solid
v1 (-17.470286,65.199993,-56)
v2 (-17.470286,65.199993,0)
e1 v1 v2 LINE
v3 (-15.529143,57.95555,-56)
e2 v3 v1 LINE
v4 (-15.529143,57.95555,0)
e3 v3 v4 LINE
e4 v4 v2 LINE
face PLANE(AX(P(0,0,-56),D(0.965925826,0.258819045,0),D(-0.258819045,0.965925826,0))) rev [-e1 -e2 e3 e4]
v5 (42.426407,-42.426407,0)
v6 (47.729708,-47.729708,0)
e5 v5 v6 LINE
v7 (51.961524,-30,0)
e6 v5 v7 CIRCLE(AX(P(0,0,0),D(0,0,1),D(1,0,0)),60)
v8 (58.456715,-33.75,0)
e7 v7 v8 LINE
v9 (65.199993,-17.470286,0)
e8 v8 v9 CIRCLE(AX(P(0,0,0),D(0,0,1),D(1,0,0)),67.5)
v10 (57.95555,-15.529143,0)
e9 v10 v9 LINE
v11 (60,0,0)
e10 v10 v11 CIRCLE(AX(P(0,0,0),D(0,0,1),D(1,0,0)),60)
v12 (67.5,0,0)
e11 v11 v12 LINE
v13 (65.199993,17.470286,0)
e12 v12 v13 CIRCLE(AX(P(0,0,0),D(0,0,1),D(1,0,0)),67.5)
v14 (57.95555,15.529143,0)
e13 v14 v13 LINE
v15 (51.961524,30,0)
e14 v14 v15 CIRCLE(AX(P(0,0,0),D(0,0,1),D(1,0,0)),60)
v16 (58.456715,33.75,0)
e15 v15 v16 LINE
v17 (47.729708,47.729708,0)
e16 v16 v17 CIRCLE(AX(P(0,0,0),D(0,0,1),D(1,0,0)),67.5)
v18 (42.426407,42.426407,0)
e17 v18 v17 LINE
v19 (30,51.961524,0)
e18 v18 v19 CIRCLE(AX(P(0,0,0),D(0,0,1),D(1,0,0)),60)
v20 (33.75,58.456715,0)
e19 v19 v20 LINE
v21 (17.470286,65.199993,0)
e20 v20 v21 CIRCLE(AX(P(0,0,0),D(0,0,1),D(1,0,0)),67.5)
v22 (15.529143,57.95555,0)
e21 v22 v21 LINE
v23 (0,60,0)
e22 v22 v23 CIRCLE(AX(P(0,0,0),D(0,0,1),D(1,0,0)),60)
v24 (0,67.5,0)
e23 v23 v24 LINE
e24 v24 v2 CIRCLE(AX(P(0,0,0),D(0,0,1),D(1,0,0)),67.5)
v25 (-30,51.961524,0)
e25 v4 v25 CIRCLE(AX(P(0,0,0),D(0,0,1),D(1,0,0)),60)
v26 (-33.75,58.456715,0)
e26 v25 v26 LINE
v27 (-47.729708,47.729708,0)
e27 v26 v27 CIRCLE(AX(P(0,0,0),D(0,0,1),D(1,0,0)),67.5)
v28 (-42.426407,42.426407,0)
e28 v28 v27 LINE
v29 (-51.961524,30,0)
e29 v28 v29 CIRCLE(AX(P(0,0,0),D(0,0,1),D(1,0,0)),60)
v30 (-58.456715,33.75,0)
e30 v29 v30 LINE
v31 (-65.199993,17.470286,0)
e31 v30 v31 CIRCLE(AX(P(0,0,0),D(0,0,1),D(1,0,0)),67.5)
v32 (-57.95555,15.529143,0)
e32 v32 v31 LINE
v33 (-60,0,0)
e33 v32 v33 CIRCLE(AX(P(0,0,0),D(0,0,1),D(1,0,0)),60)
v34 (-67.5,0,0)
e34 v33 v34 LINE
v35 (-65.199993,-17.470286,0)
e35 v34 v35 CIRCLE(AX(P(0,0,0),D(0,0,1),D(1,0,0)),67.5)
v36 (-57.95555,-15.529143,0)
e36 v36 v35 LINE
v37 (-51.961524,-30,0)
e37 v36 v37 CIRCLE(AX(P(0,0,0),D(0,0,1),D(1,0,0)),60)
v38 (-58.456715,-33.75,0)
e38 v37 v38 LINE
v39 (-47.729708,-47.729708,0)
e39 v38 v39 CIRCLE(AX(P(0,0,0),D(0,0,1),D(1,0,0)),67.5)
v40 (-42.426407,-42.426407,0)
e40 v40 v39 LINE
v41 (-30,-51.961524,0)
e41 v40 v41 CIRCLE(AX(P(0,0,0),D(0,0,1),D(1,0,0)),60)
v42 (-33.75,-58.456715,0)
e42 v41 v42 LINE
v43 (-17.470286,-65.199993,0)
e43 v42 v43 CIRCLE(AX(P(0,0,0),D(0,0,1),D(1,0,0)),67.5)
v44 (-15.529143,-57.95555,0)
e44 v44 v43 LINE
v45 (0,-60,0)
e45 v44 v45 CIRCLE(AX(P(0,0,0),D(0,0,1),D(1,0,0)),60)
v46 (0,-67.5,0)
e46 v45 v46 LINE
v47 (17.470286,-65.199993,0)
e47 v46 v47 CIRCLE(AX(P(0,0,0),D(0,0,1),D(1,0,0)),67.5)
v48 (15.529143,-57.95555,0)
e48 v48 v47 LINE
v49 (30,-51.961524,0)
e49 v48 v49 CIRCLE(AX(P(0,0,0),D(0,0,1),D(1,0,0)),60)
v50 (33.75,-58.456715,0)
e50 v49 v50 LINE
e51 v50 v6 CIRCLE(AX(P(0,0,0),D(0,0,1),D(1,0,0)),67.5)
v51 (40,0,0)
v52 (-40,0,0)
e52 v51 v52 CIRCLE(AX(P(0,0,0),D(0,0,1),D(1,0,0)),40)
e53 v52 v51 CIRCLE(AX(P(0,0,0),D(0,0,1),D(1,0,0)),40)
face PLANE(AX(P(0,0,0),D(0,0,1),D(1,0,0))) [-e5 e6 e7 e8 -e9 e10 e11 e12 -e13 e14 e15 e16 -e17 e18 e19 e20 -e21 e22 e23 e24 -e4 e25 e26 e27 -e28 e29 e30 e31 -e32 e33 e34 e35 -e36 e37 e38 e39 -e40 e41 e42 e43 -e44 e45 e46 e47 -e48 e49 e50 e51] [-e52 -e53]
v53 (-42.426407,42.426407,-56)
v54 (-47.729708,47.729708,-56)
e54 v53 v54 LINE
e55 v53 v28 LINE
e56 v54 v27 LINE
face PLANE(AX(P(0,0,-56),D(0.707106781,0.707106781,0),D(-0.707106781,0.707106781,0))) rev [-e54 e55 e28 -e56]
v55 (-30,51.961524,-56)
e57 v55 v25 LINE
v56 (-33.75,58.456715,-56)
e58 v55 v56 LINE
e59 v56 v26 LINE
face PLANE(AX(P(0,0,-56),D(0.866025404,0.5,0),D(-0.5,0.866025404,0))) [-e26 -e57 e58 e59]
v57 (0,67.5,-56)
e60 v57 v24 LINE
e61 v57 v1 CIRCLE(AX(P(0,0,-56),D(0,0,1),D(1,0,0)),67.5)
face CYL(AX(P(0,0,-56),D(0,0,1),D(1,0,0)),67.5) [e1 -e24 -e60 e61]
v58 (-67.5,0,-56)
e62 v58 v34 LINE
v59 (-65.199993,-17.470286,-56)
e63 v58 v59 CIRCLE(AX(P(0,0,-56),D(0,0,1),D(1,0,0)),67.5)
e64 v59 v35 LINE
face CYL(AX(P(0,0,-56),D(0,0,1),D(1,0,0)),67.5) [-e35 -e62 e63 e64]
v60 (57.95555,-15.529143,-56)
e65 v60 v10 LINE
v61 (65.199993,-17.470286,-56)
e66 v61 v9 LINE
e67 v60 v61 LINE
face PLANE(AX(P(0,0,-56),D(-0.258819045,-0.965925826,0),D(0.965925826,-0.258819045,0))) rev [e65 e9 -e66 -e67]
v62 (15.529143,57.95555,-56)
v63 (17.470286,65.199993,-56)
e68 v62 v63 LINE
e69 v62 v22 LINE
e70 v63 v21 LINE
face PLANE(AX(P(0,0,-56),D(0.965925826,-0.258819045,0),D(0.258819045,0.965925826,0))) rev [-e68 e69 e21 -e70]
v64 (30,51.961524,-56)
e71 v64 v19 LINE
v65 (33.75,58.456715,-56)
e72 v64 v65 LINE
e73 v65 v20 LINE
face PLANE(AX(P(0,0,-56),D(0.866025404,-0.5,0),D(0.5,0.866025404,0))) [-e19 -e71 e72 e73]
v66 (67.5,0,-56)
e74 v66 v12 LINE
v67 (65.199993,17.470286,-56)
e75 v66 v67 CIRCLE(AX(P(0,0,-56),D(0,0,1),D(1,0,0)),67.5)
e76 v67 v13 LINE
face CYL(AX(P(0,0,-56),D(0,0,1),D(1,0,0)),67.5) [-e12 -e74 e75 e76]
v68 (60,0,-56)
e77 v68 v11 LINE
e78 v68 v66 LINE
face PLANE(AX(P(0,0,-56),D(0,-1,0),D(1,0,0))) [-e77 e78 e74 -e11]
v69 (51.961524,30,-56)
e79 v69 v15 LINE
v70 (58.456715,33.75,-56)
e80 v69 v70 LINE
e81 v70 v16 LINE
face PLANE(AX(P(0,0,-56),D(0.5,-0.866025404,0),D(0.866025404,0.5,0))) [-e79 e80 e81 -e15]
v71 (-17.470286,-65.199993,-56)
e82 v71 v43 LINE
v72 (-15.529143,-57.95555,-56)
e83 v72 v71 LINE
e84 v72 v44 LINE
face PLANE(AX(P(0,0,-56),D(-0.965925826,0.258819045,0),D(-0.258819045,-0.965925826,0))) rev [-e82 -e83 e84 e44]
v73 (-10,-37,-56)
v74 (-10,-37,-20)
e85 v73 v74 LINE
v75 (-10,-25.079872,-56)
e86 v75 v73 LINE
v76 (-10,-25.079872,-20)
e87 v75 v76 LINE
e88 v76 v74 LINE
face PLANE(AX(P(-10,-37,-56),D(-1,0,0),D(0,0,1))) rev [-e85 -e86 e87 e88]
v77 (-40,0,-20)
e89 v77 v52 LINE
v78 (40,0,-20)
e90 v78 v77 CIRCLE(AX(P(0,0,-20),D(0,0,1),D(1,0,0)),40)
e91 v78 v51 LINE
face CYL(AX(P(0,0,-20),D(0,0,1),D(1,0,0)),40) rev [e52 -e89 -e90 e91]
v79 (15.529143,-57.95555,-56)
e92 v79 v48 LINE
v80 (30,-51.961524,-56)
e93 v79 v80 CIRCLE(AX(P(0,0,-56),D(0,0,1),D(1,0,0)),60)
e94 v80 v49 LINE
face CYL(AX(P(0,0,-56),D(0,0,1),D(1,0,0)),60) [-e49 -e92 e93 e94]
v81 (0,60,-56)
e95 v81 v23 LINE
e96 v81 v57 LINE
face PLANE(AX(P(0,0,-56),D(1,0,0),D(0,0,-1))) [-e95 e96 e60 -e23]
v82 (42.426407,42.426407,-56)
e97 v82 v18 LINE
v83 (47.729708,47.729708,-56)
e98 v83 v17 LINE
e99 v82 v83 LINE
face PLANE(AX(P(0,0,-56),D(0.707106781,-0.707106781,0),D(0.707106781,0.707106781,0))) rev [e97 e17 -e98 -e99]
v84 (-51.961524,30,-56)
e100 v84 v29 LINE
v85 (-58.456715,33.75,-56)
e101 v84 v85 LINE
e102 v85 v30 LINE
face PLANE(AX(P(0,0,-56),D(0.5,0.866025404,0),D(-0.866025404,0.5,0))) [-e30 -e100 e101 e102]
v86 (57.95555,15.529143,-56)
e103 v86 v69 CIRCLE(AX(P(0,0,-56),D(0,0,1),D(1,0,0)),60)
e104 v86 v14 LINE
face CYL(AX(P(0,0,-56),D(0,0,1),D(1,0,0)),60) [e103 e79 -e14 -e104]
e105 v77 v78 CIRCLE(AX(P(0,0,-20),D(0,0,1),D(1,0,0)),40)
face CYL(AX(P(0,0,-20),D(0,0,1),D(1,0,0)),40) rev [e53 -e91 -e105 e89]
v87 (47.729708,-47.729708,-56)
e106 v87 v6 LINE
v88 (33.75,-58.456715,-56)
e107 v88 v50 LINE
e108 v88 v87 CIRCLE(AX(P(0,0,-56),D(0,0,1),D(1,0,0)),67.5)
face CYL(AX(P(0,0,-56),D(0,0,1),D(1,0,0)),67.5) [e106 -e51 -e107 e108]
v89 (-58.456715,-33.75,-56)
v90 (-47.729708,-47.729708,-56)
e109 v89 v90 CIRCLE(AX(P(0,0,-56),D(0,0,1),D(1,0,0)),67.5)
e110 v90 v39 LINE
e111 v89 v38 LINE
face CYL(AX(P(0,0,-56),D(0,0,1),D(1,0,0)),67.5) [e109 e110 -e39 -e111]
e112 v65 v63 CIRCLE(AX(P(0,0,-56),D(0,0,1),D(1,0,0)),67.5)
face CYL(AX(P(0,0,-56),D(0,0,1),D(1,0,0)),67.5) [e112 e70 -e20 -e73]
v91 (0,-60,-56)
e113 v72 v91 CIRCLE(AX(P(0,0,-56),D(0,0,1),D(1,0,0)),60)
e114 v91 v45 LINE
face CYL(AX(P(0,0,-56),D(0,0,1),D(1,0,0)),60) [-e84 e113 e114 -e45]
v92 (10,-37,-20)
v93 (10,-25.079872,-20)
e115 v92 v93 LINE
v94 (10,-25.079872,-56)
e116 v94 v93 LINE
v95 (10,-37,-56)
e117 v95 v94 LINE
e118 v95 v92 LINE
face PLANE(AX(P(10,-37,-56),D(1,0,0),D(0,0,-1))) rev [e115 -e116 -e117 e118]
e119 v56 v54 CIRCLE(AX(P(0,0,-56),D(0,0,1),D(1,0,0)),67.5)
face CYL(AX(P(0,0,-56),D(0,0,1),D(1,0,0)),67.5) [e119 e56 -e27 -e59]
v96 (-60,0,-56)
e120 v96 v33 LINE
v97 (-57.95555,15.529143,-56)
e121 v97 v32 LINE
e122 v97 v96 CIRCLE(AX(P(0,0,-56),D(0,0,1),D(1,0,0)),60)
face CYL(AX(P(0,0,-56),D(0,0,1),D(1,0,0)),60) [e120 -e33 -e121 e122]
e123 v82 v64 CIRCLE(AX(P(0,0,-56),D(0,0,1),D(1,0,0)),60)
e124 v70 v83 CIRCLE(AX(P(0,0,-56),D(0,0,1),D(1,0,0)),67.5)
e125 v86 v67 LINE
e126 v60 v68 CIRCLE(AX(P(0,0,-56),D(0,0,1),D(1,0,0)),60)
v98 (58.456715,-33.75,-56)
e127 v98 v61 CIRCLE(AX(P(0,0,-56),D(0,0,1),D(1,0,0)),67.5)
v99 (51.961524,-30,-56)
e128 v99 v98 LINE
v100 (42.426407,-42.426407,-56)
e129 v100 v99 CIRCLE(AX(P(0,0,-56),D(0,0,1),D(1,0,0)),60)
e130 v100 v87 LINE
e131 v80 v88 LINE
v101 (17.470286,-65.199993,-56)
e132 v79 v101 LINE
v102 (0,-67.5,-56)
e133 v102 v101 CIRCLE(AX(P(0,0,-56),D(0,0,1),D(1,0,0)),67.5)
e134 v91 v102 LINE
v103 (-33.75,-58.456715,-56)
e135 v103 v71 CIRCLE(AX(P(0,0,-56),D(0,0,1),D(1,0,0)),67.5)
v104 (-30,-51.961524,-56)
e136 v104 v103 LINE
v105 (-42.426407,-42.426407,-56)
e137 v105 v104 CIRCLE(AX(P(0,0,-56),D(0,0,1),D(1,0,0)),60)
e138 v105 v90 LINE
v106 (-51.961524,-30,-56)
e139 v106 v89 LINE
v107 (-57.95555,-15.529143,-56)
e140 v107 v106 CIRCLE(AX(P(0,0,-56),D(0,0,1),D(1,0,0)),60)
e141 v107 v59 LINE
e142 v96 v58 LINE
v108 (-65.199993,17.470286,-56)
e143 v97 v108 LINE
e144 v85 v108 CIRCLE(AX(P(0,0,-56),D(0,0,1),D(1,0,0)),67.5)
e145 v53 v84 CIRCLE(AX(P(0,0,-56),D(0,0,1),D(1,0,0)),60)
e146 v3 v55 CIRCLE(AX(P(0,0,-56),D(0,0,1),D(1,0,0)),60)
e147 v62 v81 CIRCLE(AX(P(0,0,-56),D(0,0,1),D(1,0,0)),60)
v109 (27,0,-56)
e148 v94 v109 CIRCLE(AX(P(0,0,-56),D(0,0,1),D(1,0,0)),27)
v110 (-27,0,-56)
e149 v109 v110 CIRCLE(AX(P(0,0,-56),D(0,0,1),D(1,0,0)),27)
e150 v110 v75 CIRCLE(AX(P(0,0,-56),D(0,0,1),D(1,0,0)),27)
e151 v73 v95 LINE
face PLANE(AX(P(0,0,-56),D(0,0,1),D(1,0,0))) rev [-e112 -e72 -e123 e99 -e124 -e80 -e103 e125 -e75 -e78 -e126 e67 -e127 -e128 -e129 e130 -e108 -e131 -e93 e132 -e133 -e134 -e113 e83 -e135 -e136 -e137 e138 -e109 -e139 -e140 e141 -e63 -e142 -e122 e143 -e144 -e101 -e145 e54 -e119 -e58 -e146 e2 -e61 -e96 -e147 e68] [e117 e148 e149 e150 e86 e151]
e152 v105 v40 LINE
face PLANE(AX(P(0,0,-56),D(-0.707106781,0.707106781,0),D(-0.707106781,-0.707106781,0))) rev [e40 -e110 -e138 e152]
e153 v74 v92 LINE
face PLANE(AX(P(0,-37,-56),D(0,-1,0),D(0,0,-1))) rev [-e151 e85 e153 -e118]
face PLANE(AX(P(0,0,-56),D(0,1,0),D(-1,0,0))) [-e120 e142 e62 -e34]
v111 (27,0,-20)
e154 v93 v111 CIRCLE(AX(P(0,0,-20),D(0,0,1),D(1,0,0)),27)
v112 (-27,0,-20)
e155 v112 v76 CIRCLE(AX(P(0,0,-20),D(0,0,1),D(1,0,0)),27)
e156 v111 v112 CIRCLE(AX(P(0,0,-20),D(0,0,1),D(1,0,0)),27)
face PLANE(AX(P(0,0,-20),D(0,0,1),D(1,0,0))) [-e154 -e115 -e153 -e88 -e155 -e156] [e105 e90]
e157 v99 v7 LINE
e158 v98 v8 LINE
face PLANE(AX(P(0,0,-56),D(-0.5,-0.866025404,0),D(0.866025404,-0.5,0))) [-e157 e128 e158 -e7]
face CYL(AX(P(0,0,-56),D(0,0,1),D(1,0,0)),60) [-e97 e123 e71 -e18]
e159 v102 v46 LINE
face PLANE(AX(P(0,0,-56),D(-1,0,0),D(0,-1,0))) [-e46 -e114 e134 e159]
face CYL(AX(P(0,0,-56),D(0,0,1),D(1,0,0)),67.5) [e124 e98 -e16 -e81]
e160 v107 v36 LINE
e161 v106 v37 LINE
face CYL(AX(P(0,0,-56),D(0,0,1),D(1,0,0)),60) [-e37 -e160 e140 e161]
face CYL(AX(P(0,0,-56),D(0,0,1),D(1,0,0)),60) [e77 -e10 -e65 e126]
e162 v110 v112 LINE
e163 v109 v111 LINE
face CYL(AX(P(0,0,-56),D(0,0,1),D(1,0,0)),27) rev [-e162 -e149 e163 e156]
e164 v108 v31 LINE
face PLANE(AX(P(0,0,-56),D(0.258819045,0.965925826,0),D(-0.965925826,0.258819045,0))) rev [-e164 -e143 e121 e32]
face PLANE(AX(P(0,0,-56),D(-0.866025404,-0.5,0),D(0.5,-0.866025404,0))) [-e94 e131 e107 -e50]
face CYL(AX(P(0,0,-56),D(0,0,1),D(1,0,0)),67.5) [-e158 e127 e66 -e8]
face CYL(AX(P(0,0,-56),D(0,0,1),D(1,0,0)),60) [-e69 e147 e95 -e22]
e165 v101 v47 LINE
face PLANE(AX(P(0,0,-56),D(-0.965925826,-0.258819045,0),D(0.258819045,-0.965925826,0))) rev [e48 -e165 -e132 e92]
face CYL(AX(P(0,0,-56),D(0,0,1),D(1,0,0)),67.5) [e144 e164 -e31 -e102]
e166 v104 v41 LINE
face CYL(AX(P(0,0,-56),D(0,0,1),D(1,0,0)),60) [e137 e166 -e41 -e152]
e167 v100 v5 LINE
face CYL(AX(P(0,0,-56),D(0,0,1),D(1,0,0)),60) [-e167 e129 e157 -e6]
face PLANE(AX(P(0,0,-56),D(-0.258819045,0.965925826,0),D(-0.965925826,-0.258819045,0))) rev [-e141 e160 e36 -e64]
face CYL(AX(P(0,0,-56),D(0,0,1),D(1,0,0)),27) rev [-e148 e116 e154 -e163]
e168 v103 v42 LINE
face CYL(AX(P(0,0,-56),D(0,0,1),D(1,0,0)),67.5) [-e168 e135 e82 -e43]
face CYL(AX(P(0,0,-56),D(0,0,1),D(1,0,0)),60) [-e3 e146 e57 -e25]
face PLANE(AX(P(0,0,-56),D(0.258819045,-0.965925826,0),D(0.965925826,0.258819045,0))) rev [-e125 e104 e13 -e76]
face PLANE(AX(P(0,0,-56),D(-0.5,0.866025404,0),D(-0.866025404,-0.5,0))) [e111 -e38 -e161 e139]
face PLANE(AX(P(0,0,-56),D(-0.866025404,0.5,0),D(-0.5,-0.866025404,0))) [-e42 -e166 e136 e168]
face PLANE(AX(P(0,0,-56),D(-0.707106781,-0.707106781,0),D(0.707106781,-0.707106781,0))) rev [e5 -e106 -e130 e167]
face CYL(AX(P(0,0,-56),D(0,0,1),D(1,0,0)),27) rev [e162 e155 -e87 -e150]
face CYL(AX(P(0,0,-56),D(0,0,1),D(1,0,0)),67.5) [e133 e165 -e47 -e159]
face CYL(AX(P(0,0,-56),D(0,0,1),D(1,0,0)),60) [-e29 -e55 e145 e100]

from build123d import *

# Parameters (mm, degrees)
GEAR_BODY_12T_DEPTH  = 56
FACE_RECESS_SKETCH_R = 40
FACE_RECESS_80_DEPTH = 20
BORE_CUT_DEPTH       = 36


with BuildPart() as part:
    # Gear Tooth Profile Sketch → Gear Body 12T (new body)
    with BuildSketch(Plane.XY):
        with BuildLine():
            Line((-15.529142706, 57.955549577), (-17.470285544, 65.199993275))
            ThreePointArc((-17.470285544, 65.199993275), (-8.810517975, 66.922528143), (0, 67.5))
            Line((0, 67.5), (0, 60))
            ThreePointArc((0, 60), (7.831571533, 59.486691682), (15.529142706, 57.955549577))
            Line((15.529142706, 57.955549577), (17.470285544, 65.199993275))
            ThreePointArc((17.470285544, 65.199993275), (25.831131685, 62.361868445), (33.75, 58.456714755))
            Line((33.75, 58.456714755), (30, 51.961524227))
            ThreePointArc((30, 51.961524227), (36.525685741, 47.601200417), (42.426406871, 42.426406871))
            Line((42.426406871, 42.426406871), (47.72970773, 47.72970773))
            ThreePointArc((47.72970773, 47.72970773), (53.55135047, 41.091396458), (58.456714755, 33.75))
            Line((58.456714755, 33.75), (51.961524227, 30))
            ThreePointArc((51.961524227, 30), (55.432771951, 22.961005942), (57.955549577, 15.529142706))
            Line((57.955549577, 15.529142706), (65.199993275, 17.470285544))
            ThreePointArc((65.199993275, 17.470285544), (66.922528143, 8.810517975), (67.5, 0))
            Line((67.5, 0), (60, 0))
            ThreePointArc((60, 0), (59.486691682, -7.831571533), (57.955549577, -15.529142706))
            Line((57.955549577, -15.529142706), (65.199993275, -17.470285544))
            ThreePointArc((65.199993275, -17.470285544), (62.361868445, -25.831131685), (58.456714755, -33.75))
            Line((58.456714755, -33.75), (51.961524227, -30))
            ThreePointArc((51.961524227, -30), (47.601200417, -36.525685741), (42.426406871, -42.426406871))
            Line((42.426406871, -42.426406871), (47.72970773, -47.72970773))
            ThreePointArc((47.72970773, -47.72970773), (41.091396458, -53.55135047), (33.75, -58.456714755))
            Line((33.75, -58.456714755), (30, -51.961524227))
            ThreePointArc((30, -51.961524227), (22.961005942, -55.432771951), (15.529142706, -57.955549577))
            Line((15.529142706, -57.955549577), (17.470285544, -65.199993275))
            ThreePointArc((17.470285544, -65.199993275), (8.810517975, -66.922528143), (0, -67.5))
            Line((0, -67.5), (0, -60))
            ThreePointArc((0, -60), (-7.831571533, -59.486691682), (-15.529142706, -57.955549577))
            Line((-15.529142706, -57.955549577), (-17.470285544, -65.199993275))
            ThreePointArc((-17.470285544, -65.199993275), (-25.831131685, -62.361868445), (-33.75, -58.456714755))
            Line((-33.75, -58.456714755), (-30, -51.961524227))
            ThreePointArc((-30, -51.961524227), (-36.525685741, -47.601200417), (-42.426406871, -42.426406871))
            Line((-42.426406871, -42.426406871), (-47.72970773, -47.72970773))
            ThreePointArc((-47.72970773, -47.72970773), (-53.55135047, -41.091396458), (-58.456714755, -33.75))
            Line((-58.456714755, -33.75), (-51.961524227, -30))
            ThreePointArc((-51.961524227, -30), (-55.432771951, -22.961005942), (-57.955549577, -15.529142706))
            Line((-57.955549577, -15.529142706), (-65.199993275, -17.470285544))
            ThreePointArc((-65.199993275, -17.470285544), (-66.922528143, -8.810517975), (-67.5, 0))
            Line((-67.5, 0), (-60, 0))
            ThreePointArc((-60, 0), (-59.486691682, 7.831571533), (-57.955549577, 15.529142706))
            Line((-57.955549577, 15.529142706), (-65.199993275, 17.470285544))
            ThreePointArc((-65.199993275, 17.470285544), (-62.361868445, 25.831131685), (-58.456714755, 33.75))
            Line((-58.456714755, 33.75), (-51.961524227, 30))
            ThreePointArc((-51.961524227, 30), (-47.601200417, 36.525685741), (-42.426406871, 42.426406871))
            Line((-42.426406871, 42.426406871), (-47.72970773, 47.72970773))
            ThreePointArc((-47.72970773, 47.72970773), (-41.091396458, 53.55135047), (-33.75, 58.456714755))
            Line((-33.75, 58.456714755), (-30, 51.961524227))
            ThreePointArc((-30, 51.961524227), (-22.961005942, 55.432771951), (-15.529142706, 57.955549577))
        make_face()
    extrude(amount=-GEAR_BODY_12T_DEPTH)

    # Face Recess Sketch → Face Recess Ø80 (cut)
    with BuildSketch(Plane.XY):
        Circle(FACE_RECESS_SKETCH_R)
    extrude(amount=-FACE_RECESS_80_DEPTH, mode=Mode.SUBTRACT)

    # Bore Profile Sketch → Bore Cut (cut)
    with BuildSketch(Plane.XY.offset(-20)):
        with BuildLine():
            Line((0, -37), (10, -37))
            Line((10, -37), (10, -25.079872408))
            ThreePointArc((10, -25.079872408), (0, 27), (-10, -25.079872408))
            Line((-10, -25.079872408), (-10, -37))
            Line((-10, -37), (0, -37))
        make_face()
    extrude(amount=-BORE_CUT_DEPTH, mode=Mode.SUBTRACT)


solid = part.part
